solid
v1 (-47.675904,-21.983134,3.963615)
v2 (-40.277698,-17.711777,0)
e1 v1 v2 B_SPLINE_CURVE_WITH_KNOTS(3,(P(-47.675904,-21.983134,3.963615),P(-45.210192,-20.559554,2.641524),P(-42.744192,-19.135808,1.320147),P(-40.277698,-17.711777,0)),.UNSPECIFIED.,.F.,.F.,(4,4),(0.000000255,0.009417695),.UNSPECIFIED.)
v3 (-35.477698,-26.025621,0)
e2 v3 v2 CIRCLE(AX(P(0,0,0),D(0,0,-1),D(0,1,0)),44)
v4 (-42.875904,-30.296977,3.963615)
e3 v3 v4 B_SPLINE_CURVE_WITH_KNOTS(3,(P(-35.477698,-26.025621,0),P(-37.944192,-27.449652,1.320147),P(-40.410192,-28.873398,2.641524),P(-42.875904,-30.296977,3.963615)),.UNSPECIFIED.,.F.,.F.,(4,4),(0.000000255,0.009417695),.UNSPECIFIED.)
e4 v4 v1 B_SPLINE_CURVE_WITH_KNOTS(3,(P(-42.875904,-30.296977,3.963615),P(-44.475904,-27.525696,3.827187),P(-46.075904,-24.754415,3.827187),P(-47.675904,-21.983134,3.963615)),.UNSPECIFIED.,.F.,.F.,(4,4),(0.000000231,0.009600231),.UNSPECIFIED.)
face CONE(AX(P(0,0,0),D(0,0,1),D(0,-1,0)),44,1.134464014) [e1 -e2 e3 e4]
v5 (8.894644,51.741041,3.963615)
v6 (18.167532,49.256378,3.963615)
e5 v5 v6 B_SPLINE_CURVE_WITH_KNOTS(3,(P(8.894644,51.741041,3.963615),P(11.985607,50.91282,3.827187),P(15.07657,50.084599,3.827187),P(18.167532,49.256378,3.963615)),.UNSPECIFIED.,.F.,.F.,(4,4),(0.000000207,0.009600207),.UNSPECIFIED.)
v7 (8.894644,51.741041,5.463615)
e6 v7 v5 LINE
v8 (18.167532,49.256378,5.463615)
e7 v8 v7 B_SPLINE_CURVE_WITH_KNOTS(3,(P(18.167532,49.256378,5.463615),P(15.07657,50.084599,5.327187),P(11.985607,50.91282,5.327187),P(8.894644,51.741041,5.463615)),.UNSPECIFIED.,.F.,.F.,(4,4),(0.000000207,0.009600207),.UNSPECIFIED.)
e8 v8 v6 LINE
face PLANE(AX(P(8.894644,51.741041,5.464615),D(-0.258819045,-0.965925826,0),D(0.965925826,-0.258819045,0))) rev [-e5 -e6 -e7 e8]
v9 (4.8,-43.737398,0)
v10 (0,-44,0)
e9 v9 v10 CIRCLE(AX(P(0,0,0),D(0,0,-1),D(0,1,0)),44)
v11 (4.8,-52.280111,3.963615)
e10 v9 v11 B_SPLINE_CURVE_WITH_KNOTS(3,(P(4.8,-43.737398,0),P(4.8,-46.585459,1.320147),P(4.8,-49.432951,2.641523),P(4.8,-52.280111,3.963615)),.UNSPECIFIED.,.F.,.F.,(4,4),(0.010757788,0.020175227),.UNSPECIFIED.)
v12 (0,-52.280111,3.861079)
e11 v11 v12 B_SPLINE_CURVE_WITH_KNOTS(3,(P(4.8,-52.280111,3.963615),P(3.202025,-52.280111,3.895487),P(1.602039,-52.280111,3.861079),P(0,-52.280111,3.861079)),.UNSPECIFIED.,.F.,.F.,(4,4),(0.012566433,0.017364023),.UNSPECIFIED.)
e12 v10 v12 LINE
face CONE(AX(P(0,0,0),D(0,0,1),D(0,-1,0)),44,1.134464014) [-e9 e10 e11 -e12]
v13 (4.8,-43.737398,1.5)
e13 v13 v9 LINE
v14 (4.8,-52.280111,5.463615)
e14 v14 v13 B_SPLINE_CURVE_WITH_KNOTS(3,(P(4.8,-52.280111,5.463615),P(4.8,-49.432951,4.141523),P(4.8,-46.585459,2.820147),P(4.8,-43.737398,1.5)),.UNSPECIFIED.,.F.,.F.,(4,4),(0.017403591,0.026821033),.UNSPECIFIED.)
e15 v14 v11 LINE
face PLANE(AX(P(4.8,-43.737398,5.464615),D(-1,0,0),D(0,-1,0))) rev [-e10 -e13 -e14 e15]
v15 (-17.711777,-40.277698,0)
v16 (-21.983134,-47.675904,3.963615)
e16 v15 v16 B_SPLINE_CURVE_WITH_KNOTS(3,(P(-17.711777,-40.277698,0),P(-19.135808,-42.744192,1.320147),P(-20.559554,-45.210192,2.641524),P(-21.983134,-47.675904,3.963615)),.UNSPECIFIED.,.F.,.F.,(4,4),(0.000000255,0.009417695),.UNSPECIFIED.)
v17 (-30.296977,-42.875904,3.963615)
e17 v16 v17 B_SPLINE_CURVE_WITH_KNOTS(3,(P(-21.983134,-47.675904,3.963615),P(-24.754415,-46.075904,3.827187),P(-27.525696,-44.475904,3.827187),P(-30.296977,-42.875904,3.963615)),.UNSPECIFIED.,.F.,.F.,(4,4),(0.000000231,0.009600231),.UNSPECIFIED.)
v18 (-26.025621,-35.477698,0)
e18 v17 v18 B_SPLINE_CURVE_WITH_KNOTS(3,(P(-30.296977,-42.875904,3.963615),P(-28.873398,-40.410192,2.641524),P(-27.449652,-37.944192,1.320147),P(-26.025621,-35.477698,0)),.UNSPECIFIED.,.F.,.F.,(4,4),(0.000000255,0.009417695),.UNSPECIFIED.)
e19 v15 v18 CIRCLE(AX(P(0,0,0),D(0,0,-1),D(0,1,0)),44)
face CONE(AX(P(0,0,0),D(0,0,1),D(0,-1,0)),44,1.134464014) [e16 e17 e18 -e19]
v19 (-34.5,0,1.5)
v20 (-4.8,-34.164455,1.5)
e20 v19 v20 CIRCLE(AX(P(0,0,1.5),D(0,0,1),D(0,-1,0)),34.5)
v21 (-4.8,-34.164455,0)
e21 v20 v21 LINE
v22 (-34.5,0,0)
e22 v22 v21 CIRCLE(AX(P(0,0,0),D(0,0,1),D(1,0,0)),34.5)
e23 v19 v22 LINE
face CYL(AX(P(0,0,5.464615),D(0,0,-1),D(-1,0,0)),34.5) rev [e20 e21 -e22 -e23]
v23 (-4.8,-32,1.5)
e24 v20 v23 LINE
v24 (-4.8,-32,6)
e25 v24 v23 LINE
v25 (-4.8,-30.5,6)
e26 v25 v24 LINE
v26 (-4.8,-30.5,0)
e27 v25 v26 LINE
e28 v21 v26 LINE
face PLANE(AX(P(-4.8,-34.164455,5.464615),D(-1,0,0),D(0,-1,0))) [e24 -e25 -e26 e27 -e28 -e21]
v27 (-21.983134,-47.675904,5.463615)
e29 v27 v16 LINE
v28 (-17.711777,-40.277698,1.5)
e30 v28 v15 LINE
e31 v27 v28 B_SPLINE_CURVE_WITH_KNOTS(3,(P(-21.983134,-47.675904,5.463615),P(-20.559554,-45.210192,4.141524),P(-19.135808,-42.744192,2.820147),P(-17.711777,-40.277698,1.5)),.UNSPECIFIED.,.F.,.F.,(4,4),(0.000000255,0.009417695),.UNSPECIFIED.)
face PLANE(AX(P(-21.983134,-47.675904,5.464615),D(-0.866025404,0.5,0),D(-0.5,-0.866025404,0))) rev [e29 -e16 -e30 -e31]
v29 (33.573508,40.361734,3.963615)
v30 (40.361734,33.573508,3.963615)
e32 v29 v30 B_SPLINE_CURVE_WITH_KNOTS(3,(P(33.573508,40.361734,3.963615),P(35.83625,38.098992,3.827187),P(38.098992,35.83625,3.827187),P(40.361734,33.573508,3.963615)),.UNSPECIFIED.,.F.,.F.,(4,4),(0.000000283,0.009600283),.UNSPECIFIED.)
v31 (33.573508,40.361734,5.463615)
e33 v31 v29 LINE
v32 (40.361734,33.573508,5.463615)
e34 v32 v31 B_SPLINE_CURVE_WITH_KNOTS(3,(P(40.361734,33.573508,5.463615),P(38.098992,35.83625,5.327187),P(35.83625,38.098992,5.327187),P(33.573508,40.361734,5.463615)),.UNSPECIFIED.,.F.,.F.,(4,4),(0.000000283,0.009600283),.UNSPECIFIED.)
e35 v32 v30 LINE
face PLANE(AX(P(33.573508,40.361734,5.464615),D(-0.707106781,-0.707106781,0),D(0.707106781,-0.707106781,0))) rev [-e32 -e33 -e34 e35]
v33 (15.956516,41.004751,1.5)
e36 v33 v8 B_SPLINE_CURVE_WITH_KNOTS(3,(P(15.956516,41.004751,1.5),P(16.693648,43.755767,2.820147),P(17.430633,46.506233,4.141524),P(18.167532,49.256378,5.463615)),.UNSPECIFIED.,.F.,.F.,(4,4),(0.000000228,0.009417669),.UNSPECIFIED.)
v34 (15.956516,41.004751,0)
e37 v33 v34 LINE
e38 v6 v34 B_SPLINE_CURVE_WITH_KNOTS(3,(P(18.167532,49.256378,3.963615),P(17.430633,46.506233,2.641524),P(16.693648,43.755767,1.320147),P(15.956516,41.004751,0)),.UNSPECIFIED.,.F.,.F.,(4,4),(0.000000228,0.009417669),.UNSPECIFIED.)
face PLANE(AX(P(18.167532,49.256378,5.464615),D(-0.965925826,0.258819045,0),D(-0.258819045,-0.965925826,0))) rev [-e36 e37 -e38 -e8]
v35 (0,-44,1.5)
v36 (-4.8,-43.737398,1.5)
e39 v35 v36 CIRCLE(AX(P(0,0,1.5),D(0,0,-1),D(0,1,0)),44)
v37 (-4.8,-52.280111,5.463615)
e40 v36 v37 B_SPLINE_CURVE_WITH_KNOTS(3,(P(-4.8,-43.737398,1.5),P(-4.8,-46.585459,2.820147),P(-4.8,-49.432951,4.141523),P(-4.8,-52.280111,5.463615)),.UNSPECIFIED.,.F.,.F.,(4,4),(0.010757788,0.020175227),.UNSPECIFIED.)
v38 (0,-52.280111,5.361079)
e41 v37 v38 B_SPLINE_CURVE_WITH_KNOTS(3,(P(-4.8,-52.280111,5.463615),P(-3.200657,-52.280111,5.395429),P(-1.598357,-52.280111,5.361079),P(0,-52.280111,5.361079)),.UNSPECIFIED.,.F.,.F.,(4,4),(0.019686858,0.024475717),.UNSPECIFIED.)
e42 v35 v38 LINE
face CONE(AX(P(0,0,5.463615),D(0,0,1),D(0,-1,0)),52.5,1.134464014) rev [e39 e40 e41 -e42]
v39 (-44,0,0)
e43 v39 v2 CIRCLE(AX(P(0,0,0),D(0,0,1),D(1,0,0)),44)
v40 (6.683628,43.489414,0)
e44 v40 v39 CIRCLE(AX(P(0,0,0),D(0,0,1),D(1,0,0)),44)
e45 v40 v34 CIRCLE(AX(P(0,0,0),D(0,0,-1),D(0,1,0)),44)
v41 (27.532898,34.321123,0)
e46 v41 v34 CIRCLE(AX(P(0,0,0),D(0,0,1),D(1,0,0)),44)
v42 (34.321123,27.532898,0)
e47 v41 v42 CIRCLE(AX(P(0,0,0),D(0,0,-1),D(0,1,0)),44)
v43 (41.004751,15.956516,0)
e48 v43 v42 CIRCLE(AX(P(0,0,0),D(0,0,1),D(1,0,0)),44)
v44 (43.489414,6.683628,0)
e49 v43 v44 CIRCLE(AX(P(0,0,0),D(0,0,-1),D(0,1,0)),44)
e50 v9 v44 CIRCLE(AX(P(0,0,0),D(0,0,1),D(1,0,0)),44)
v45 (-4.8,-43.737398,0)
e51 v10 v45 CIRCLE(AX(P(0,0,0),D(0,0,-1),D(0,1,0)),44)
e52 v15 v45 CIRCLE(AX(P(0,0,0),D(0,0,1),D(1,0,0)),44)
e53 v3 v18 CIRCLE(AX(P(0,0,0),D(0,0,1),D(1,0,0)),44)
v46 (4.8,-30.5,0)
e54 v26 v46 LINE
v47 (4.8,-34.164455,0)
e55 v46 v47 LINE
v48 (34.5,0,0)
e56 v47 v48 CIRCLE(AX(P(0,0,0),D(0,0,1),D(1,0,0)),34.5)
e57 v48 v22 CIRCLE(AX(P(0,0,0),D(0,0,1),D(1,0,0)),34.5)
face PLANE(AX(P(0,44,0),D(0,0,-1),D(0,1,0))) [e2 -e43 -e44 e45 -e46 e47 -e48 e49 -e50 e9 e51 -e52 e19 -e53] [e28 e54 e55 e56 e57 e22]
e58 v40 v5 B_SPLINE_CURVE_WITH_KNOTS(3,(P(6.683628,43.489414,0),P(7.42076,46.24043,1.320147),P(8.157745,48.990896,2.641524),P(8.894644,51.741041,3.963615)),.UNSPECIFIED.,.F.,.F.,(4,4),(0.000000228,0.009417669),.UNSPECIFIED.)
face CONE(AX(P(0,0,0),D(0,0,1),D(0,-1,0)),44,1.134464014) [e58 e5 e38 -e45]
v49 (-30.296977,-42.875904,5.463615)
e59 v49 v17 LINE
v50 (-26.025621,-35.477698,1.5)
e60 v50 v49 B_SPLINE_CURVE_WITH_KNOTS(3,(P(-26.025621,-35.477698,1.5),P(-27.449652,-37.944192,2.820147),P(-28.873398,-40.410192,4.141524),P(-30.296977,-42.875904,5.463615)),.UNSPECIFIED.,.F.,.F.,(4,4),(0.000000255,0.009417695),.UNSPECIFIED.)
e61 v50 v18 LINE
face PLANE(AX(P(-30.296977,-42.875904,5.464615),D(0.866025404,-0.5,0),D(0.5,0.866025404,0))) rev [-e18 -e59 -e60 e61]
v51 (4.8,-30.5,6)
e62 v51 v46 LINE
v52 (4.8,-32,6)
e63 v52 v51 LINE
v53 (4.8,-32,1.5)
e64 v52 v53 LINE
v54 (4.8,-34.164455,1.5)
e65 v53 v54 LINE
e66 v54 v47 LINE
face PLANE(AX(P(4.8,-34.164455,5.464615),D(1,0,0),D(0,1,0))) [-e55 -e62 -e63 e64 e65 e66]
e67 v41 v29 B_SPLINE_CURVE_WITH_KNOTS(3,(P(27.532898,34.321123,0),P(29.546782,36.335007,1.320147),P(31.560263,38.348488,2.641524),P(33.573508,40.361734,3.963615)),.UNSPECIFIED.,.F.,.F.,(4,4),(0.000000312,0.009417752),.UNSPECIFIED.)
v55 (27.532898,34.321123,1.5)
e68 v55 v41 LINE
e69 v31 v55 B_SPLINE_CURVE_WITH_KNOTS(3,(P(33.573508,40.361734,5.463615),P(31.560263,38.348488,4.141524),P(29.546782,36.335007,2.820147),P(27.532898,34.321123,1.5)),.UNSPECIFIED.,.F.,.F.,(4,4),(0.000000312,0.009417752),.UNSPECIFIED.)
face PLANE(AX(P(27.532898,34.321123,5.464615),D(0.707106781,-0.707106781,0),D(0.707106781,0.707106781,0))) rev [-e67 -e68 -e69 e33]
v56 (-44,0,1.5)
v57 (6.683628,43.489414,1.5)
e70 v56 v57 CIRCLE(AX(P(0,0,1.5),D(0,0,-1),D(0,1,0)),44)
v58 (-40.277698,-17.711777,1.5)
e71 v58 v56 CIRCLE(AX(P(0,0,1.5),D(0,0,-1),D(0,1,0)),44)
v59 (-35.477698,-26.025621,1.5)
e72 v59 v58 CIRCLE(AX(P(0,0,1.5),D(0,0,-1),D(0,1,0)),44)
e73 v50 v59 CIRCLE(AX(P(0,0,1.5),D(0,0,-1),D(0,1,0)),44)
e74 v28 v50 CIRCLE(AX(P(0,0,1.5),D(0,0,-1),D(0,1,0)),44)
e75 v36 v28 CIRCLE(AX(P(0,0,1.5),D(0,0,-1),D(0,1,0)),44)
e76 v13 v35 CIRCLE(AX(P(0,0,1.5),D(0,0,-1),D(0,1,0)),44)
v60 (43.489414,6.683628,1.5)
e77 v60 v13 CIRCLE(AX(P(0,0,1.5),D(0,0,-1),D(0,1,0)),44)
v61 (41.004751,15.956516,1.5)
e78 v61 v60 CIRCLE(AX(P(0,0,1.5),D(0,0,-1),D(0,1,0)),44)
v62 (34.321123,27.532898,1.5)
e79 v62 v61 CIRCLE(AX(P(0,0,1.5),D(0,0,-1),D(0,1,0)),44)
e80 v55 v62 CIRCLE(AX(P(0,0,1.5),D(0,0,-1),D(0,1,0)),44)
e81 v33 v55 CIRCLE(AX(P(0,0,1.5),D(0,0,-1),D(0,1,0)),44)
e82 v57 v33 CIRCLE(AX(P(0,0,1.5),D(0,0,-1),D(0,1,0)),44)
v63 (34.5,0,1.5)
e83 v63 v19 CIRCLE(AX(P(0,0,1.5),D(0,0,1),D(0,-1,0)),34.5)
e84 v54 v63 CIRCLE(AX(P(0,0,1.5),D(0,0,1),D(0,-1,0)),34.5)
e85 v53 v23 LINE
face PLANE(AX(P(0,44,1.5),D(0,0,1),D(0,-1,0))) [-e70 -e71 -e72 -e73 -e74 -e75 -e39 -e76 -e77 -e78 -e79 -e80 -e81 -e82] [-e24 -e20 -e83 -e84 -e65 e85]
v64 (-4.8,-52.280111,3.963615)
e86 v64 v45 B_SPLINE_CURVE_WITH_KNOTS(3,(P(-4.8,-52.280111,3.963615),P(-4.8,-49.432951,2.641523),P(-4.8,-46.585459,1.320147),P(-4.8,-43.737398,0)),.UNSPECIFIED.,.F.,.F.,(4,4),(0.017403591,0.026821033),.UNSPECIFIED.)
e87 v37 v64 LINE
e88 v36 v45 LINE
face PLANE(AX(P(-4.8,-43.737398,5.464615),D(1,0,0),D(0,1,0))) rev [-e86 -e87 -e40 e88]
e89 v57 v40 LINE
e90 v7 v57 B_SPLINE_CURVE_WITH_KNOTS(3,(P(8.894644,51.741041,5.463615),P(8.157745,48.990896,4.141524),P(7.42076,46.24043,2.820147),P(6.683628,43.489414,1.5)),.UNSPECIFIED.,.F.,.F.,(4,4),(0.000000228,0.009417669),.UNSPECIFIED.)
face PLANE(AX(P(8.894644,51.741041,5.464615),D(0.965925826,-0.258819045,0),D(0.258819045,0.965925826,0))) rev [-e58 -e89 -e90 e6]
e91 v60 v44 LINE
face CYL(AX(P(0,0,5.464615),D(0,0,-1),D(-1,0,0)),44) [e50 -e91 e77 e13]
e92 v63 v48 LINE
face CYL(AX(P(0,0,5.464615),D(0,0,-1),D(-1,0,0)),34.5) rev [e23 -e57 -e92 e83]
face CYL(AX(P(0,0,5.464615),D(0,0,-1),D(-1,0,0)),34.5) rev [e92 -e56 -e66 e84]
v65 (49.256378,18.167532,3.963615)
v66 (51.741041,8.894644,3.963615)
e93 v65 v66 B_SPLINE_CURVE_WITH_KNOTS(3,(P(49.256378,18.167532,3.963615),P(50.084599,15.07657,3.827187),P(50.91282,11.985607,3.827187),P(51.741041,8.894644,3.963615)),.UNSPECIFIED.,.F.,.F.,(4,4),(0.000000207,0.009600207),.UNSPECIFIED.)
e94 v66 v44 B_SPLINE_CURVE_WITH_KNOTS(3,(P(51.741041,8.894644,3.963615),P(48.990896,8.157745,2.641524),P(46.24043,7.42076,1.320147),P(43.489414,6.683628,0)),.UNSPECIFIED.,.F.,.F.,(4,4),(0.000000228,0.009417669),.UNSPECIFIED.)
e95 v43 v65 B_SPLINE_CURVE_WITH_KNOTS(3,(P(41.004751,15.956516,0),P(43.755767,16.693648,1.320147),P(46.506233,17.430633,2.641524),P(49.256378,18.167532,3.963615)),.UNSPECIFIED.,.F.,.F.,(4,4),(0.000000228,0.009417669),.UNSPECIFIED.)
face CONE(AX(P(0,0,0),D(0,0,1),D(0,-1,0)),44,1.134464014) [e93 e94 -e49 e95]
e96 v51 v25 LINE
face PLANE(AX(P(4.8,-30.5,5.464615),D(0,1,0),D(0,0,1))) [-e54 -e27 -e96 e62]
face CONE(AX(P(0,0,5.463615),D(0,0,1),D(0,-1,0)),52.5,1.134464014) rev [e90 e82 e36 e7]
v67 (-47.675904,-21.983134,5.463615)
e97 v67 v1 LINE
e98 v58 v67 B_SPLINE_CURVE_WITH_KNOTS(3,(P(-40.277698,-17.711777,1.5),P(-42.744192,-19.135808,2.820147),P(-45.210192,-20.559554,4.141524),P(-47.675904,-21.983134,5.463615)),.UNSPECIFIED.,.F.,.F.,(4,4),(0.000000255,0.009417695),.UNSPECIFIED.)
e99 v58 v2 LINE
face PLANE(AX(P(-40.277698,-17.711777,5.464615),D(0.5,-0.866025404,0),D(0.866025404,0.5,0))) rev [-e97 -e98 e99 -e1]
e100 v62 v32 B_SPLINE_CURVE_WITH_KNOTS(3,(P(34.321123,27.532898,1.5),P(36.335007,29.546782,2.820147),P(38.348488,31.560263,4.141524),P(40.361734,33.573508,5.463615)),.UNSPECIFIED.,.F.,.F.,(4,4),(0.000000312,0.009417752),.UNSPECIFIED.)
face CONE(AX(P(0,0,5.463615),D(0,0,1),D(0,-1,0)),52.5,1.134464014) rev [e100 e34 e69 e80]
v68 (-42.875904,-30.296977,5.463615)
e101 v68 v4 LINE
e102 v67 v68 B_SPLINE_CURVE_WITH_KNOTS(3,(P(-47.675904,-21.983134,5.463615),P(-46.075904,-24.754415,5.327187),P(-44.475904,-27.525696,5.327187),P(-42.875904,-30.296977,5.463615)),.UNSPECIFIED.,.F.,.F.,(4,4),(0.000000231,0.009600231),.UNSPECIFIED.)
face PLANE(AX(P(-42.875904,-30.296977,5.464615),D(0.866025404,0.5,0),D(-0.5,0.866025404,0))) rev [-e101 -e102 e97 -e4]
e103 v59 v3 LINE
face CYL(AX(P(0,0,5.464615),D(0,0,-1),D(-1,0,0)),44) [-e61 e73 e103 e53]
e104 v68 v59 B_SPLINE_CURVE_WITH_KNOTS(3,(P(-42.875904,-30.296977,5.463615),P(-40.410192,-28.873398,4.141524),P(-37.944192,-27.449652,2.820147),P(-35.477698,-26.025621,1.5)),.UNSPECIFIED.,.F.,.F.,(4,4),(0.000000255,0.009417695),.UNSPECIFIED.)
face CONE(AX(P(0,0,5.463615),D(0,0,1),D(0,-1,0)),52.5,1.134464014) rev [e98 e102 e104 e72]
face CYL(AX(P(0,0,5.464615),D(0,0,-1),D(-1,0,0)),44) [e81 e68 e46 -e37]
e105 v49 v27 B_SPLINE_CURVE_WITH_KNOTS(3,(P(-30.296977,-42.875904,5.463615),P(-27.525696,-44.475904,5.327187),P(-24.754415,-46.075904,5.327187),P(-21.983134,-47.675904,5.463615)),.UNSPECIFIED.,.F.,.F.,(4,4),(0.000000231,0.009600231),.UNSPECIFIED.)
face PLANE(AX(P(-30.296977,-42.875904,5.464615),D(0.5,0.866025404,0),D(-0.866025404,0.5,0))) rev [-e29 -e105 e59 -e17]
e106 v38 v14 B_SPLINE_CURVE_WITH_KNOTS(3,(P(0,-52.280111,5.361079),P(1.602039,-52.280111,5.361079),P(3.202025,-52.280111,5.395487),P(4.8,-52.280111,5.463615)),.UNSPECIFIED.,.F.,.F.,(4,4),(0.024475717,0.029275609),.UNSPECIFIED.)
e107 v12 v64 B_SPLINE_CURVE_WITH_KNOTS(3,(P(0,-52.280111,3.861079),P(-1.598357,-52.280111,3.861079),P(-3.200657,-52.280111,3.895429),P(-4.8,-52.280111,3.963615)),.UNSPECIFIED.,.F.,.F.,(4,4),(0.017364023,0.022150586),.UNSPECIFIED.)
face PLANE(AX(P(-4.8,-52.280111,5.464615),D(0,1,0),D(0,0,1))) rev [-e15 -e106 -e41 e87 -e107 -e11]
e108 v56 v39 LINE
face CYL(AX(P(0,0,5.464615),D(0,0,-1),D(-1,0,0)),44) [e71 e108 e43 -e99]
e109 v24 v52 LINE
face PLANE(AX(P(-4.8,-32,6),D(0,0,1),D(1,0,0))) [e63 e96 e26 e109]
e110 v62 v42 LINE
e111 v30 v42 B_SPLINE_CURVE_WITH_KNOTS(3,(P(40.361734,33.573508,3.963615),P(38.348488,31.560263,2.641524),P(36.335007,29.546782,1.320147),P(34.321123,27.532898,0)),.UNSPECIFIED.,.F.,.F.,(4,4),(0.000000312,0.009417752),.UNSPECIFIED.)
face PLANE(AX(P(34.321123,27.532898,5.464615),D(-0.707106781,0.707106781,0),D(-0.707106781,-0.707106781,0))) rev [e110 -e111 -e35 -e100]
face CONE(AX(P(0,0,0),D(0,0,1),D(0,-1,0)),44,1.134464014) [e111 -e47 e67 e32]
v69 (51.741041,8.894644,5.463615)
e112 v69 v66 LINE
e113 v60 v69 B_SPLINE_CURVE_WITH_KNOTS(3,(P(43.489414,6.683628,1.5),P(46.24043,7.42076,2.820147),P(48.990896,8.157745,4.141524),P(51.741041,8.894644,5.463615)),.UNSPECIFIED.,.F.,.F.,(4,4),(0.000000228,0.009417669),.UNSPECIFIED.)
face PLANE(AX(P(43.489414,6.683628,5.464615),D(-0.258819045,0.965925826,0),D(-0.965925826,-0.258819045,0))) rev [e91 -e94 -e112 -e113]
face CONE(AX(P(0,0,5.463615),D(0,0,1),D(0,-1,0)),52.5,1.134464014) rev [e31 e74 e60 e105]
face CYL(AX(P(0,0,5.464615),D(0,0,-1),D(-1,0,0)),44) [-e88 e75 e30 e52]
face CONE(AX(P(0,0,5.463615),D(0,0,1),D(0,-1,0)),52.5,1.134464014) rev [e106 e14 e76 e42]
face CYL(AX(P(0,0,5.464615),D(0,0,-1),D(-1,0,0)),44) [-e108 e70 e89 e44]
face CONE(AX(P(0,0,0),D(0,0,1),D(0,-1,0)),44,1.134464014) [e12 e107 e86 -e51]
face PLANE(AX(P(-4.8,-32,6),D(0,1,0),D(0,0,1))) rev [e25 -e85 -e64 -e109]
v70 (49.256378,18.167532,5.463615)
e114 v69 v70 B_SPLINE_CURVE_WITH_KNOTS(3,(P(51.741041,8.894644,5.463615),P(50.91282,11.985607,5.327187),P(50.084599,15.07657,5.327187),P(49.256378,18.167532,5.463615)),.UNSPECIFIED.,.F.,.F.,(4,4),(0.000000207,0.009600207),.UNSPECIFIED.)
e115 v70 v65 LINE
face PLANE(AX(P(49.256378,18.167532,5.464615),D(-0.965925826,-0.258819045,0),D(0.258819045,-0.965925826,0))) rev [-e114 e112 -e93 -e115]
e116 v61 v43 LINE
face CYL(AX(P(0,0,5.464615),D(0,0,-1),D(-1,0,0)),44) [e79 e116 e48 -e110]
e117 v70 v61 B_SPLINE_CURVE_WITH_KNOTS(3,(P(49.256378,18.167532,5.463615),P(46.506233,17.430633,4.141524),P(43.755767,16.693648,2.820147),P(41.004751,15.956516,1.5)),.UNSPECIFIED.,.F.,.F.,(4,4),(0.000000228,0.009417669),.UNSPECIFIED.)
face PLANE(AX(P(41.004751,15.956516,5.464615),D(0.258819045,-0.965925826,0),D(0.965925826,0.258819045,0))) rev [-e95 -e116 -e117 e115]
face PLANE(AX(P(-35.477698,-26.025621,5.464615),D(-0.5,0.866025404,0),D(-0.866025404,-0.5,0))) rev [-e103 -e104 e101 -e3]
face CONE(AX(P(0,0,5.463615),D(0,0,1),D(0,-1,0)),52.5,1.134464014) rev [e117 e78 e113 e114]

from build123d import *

# Parameters (mm, degrees)
SKETCH3_OUTSIDE_W   = 136.718
SKETCH3_OUTSIDE_H   = 136.718
CUT_EXTRUDE2_DEPTH  = 5.463617
SKETCH4_W           = 9.6
SKETCH4_H           = 1.5
BOSS_EXTRUDE1_DEPTH = 6


with BuildPart() as part:
    # Sketch2 → Base-Revolve (revolve)
    with BuildSketch(Plane(origin=(0, 0, 0), x_dir=(0, 0, -1), z_dir=(1, 0, 0))):
        Polygon((-3.963615094, 52.5), (0, 44), (0, 0), (-1.5, 0), (-1.5, 44), (-5.463615094, 52.5), align=None)
    revolve(axis=Axis((0, 0, 0), (0, 0, 1)))

    # Sketch3 outside → Cut-Extrude2 (cut)
    # profile 1 of 2: a face of its own
    with BuildSketch(Plane.XY):
        Rectangle(SKETCH3_OUTSIDE_W, SKETCH3_OUTSIDE_H)
        with BuildLine():
            Line((-4.8, -43.737398185), (-4.8, -52.280110941))
            Line((-4.8, -52.280110941), (4.8, -52.280110941))
            Line((4.8, -52.280110941), (4.8, -43.737398185))
            ThreePointArc((4.8, -43.737398185), (34.907546973, -26.785502876), (43.489413898, 6.683627667))
            Line((43.489413898, 6.683627667), (51.741040776, 8.894644425))
            Line((51.741040776, 8.894644425), (49.256377943, 18.167532358))
            Line((49.256377943, 18.167532358), (41.004751065, 15.9565156))
            ThreePointArc((41.004751065, 15.9565156), (38.105117767, 22), (34.321123398, 27.532898298))
            Line((34.321123398, 27.532898298), (40.361733517, 33.573508418))
            Line((40.361733517, 33.573508418), (33.573508418, 40.361733517))
            Line((33.573508418, 40.361733517), (27.532898298, 34.321123398))
            ThreePointArc((27.532898298, 34.321123398), (22, 38.105117767), (15.9565156, 41.004751065))
            Line((15.9565156, 41.004751065), (18.167532358, 49.256377943))
            Line((18.167532358, 49.256377943), (8.894644425, 51.741040776))
            Line((8.894644425, 51.741040776), (6.683627667, 43.489413898))
            ThreePointArc((6.683627667, 43.489413898), (-34.907546973, 26.785502876), (-40.277697924, -17.711777154))
            Line((-40.277697924, -17.711777154), (-47.675904188, -21.983133532))
            Line((-47.675904188, -21.983133532), (-42.875904188, -30.296977409))
            Line((-42.875904188, -30.296977409), (-35.477697924, -26.025621031))
            ThreePointArc((-35.477697924, -26.025621031), (-31.112698372, -31.112698372), (-26.025621031, -35.477697924))
            Line((-26.025621031, -35.477697924), (-30.296977409, -42.875904188))
            Line((-30.296977409, -42.875904188), (-21.983133532, -47.675904188))
            Line((-21.983133532, -47.675904188), (-17.711777154, -40.277697924))
            ThreePointArc((-17.711777154, -40.277697924), (-11.388037985, -42.500736357), (-4.8, -43.737398185))
        make_face(mode=Mode.SUBTRACT)
    # profile 2 of 2: a face of its own
    with BuildSketch(Plane.XY):
        with BuildLine():
            Line((4.8, -34.164455213), (4.8, -30.5))
            Line((4.8, -30.5), (-4.8, -30.5))
            Line((-4.8, -30.5), (-4.8, -34.164455213))
            ThreePointArc((-4.8, -34.164455213), (0, 34.5), (4.8, -34.164455213))
        make_face()
    extrude(amount=CUT_EXTRUDE2_DEPTH, mode=Mode.SUBTRACT)

    # Sketch4 → Boss-Extrude1 (add)
    with BuildSketch(Plane.XY):
        with Locations((0, -31.25)):
            Rectangle(SKETCH4_W, SKETCH4_H)
    extrude(amount=BOSS_EXTRUDE1_DEPTH)


solid = part.part
